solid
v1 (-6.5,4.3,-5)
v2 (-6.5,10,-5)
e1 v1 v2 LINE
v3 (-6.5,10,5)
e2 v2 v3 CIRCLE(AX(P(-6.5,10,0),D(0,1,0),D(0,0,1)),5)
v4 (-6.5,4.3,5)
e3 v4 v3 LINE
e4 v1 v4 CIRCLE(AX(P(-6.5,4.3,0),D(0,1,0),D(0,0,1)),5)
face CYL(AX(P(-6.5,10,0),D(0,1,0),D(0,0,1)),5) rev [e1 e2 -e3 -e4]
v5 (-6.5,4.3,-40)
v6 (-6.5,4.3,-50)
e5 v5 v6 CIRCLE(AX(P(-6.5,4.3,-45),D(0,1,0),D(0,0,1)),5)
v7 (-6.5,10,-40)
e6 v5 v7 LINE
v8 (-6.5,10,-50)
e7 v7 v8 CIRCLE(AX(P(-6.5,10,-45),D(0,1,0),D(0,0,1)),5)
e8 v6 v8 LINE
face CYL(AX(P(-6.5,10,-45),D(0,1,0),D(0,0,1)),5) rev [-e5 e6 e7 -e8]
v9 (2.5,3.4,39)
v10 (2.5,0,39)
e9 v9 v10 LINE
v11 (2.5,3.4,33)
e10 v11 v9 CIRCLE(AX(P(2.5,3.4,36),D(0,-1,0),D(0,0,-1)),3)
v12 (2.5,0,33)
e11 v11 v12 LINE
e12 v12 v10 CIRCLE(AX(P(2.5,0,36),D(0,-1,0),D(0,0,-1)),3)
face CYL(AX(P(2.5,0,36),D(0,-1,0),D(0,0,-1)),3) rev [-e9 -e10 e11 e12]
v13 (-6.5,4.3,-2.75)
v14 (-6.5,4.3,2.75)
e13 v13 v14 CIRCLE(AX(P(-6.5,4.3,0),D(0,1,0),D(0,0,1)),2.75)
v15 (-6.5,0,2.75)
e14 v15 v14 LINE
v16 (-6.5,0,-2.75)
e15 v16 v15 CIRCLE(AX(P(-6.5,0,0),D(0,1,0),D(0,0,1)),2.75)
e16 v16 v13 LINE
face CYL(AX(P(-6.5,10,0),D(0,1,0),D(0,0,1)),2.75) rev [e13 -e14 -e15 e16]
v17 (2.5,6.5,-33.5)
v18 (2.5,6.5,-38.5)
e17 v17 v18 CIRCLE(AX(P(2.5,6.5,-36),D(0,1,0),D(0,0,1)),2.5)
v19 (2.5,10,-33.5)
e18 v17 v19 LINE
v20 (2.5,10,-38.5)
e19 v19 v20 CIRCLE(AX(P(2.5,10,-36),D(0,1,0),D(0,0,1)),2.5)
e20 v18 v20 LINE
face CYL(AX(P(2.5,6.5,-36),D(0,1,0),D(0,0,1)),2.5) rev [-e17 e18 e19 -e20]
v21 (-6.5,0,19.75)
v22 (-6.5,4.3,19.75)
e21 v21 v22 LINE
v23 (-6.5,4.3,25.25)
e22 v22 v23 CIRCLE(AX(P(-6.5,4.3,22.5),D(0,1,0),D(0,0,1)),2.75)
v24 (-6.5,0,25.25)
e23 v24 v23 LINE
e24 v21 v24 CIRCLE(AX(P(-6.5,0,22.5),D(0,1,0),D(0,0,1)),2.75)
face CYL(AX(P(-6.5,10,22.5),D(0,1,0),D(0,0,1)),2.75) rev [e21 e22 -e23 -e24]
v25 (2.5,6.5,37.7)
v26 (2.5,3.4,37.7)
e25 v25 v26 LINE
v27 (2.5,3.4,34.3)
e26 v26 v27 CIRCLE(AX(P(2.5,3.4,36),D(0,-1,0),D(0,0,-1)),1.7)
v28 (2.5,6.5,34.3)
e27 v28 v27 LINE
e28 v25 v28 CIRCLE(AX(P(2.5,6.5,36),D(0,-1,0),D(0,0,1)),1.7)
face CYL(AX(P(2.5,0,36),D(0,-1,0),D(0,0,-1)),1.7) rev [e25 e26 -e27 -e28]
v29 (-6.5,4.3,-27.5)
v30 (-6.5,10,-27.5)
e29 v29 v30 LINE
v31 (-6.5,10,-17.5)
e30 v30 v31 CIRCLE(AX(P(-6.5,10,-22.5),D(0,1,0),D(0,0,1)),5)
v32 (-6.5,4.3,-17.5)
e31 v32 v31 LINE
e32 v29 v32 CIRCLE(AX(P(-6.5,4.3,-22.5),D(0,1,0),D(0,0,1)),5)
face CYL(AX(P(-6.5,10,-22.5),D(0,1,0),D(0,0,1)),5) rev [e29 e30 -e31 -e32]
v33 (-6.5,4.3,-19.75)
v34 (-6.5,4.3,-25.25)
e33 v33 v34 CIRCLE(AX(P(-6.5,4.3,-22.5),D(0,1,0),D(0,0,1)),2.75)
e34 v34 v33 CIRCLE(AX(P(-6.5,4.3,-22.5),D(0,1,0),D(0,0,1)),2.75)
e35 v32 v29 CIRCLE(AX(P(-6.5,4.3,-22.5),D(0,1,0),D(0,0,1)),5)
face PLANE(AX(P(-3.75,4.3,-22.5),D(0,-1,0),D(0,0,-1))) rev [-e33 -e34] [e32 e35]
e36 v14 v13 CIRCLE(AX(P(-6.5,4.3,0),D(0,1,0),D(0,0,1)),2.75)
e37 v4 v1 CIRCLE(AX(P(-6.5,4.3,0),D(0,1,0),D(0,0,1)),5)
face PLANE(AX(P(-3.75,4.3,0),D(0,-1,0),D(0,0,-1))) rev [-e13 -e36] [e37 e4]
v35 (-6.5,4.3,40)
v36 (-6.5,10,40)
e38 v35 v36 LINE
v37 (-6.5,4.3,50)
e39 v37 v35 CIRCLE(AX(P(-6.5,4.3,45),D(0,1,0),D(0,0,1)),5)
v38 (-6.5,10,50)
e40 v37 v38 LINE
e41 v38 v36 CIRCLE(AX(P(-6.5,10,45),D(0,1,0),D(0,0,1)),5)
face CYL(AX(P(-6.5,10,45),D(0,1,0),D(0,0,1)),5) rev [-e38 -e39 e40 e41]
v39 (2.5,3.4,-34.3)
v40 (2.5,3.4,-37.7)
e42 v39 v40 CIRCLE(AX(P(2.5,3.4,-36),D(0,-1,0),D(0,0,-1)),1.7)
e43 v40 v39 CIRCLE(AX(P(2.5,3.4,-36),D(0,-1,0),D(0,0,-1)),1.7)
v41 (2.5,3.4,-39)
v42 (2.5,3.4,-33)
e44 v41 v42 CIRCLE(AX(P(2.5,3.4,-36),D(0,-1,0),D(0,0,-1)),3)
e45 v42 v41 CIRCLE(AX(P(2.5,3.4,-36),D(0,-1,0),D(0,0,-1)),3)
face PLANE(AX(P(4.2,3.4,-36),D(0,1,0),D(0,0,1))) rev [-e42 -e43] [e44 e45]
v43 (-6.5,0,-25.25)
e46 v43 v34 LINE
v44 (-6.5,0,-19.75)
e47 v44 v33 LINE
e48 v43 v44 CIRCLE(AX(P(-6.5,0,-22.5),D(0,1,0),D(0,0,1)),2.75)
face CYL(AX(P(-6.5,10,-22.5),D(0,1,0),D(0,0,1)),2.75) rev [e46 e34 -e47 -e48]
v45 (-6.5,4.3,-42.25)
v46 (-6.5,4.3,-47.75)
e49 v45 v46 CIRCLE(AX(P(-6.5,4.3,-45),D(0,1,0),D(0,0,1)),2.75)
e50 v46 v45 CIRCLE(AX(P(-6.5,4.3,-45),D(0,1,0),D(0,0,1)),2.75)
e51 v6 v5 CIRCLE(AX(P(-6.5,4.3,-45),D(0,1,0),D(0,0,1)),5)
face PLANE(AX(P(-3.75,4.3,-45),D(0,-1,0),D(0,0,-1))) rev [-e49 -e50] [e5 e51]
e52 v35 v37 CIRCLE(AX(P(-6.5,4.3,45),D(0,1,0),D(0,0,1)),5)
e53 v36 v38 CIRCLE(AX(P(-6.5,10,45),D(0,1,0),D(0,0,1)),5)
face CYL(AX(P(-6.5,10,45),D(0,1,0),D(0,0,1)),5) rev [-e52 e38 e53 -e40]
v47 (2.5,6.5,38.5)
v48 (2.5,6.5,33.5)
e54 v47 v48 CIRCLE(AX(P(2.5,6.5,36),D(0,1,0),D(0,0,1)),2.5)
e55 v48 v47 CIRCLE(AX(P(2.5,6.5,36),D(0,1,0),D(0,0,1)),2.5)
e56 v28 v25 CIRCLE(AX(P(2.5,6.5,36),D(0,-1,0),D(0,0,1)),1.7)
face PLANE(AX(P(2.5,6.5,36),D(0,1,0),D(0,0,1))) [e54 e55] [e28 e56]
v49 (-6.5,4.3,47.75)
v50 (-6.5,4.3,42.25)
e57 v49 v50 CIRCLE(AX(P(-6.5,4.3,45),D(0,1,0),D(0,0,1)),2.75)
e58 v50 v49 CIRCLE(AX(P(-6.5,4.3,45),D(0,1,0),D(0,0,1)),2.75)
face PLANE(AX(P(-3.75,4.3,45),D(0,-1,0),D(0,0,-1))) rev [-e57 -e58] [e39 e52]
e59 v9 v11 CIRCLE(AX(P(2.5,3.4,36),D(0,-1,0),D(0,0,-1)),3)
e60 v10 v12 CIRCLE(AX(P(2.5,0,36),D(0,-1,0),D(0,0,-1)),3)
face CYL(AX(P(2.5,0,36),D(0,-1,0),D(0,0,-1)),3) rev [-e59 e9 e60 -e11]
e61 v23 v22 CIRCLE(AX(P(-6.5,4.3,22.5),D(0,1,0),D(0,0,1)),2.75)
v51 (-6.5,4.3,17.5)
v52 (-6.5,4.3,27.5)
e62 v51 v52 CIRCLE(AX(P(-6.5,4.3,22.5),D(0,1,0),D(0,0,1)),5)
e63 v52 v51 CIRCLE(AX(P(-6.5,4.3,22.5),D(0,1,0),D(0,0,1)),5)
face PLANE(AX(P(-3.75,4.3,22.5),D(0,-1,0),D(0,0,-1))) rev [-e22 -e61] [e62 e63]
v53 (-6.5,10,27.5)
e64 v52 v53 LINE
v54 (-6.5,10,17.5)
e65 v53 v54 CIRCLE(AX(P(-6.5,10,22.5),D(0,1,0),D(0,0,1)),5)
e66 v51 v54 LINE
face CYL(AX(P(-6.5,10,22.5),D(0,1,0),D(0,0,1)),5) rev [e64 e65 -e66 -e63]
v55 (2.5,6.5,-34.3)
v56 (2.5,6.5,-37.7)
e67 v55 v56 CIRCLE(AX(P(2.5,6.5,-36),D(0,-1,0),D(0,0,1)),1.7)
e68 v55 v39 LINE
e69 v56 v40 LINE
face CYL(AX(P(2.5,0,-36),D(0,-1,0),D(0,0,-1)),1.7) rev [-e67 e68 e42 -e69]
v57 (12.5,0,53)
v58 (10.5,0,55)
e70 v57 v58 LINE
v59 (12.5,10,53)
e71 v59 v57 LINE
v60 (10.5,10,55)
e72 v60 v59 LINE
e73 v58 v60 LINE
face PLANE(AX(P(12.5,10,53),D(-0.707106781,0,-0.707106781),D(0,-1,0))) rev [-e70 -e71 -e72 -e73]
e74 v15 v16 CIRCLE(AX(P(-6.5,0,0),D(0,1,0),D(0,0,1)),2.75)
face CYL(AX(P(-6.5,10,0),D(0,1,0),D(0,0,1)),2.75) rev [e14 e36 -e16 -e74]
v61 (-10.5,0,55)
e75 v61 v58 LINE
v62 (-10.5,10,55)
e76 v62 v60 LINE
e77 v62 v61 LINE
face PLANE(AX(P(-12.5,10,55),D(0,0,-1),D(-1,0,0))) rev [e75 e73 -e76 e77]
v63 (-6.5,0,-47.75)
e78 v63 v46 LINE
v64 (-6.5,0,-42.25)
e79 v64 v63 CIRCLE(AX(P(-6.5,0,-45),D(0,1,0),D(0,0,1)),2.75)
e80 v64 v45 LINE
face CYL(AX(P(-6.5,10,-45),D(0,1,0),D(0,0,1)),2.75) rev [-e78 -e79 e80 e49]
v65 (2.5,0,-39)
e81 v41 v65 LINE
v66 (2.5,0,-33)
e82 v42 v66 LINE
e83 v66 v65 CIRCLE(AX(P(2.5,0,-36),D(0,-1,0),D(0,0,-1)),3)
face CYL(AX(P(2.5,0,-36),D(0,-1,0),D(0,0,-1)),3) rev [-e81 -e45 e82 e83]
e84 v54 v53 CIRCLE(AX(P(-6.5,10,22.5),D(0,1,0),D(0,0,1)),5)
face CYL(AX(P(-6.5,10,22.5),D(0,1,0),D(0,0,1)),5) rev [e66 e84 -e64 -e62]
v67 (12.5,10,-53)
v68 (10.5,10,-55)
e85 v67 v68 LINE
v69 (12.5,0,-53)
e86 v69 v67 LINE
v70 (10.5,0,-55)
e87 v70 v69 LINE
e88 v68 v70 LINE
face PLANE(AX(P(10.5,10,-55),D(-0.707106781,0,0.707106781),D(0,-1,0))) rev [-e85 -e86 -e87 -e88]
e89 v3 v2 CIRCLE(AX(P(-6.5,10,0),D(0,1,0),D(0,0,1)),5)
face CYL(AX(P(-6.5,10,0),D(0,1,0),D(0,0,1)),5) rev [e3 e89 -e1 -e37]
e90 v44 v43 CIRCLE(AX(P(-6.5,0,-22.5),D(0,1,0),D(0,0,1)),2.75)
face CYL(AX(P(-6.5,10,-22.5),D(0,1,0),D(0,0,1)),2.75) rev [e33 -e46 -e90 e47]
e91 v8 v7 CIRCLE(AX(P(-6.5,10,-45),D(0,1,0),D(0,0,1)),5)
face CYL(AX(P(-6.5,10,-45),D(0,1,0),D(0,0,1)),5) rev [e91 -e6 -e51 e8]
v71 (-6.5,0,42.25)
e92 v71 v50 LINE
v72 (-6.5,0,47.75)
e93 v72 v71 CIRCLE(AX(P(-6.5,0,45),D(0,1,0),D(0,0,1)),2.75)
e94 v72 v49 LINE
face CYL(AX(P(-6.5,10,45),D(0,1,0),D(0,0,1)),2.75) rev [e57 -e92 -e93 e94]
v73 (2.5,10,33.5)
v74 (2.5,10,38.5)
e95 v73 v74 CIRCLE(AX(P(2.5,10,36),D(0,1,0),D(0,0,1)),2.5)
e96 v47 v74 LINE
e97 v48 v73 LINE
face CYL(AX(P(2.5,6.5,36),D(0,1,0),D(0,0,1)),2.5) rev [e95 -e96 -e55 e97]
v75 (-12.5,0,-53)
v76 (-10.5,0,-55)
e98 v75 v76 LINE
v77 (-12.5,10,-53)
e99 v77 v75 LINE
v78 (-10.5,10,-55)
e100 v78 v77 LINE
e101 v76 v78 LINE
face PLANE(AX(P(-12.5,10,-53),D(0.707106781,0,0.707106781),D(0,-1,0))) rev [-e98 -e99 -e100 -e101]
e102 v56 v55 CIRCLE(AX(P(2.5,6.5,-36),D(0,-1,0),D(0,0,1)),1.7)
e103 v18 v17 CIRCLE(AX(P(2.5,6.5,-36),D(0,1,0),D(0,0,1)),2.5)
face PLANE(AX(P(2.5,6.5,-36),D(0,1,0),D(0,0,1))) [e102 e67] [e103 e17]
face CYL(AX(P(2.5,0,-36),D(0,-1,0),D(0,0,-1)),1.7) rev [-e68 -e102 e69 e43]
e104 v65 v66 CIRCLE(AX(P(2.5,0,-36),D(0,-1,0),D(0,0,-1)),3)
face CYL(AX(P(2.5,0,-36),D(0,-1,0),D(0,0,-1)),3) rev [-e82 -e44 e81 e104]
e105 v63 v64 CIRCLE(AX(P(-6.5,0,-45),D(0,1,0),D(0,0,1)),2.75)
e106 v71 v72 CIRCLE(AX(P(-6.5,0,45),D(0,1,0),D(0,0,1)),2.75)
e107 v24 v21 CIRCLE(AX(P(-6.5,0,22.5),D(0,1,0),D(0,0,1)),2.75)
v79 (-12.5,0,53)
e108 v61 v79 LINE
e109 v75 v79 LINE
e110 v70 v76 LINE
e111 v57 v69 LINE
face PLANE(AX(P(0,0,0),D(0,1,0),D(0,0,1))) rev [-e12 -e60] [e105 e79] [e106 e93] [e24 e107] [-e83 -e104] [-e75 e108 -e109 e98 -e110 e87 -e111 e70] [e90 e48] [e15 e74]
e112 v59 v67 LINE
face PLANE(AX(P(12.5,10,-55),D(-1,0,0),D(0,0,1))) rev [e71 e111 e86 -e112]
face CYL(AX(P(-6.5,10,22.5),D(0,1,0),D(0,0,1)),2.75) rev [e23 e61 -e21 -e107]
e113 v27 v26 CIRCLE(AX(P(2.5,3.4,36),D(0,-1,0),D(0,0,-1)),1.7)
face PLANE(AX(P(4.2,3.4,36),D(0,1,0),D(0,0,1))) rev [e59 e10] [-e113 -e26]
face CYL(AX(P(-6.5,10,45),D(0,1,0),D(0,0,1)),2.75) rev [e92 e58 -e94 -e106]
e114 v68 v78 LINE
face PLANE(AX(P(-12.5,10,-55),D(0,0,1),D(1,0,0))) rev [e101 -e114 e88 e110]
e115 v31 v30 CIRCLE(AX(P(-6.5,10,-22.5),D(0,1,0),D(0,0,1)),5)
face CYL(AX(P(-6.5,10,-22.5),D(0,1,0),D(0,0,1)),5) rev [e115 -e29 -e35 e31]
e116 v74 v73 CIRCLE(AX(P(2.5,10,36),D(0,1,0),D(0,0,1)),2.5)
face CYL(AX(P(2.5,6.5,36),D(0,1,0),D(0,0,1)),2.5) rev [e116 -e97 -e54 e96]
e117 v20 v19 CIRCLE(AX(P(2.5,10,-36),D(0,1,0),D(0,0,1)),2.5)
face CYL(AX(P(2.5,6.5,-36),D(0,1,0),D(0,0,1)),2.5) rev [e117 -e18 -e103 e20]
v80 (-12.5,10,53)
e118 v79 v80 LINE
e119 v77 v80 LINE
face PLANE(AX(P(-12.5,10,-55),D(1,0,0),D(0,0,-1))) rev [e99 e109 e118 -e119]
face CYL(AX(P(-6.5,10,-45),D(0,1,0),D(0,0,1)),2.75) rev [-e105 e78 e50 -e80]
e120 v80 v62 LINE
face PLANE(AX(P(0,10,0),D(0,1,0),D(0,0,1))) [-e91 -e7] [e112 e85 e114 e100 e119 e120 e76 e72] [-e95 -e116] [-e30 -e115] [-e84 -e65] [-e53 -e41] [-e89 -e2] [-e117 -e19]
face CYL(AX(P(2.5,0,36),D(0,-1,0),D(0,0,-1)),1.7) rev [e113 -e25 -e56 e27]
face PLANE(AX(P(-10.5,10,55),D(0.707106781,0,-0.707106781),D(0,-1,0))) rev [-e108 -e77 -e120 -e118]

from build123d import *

# Parameters (mm, degrees)
SKETCH_1_W                  = 25
SKETCH_1_H                  = 110
EXTRUDE_1_DEPTH             = 10
CHAMFER_1_SIZE              = 2
HOLE_WIZARD_1_D             = 5.5
HOLE_WIZARD_1_DEPTH         = 12.4
HOLE_WIZARD_1_CBORE_D       = 10
HOLE_WIZARD_1_CBORE_DEPTH   = 5.7
HOLE_WIZARD_1_TIP           = 1.652366702
HOLE_WIZARD_1_2_D           = 3.4
HOLE_WIZARD_1_2_DEPTH       = 15
HOLE_WIZARD_1_2_CBORE_D     = 6
HOLE_WIZARD_1_2_CBORE_DEPTH = 3.4
HOLE_WIZARD_1_2_TIP         = 1.021463052
SKETCH_6_R                  = 2.5
CUT_EXTRUDE_1_DEPTH         = 3.5


with BuildPart() as part:
    # 草图1 → 凸台-拉伸1 (new body)
    with BuildSketch(Plane(origin=(0, 0, 0), x_dir=(1, 0, 0), z_dir=(0, 1, 0))):
        Rectangle(SKETCH_1_W, SKETCH_1_H)
    extrude(amount=EXTRUDE_1_DEPTH)

    # 倒角1
    chamfer_1_edges = [part.edges().sort_by_distance(p)[0] for p in [
        (12.5, 5, 55),
        (-12.5, 5, 55),
        (-12.5, 5, -55),
        (12.5, 5, -55),
    ]]
    chamfer(chamfer_1_edges, length=CHAMFER_1_SIZE)

    # Hole Wizard 1
    with Locations(Plane(origin=(0, 10, 0), x_dir=(1, 0, 0), z_dir=(0, 1, 0))):
        with Locations((-6.5, -45), (-6.5, 0), (-6.5, 45), (-6.5, -22.5), (-6.5, 22.5)):
            CounterBoreHole(HOLE_WIZARD_1_D / 2, HOLE_WIZARD_1_CBORE_D / 2, HOLE_WIZARD_1_CBORE_DEPTH, depth=HOLE_WIZARD_1_DEPTH)
            with Locations((0, 0, -(HOLE_WIZARD_1_DEPTH + HOLE_WIZARD_1_TIP / 2))):  # 118° drill point
                Cone(0, HOLE_WIZARD_1_D / 2, HOLE_WIZARD_1_TIP, mode=Mode.SUBTRACT)

    # Hole Wizard 1 2
    with Locations(Plane(origin=(0, 0, 0), x_dir=(-1, 0, 0), z_dir=(0, -1, 0))):
        with Locations((-2.5, -36), (-2.5, 36)):
            CounterBoreHole(HOLE_WIZARD_1_2_D / 2, HOLE_WIZARD_1_2_CBORE_D / 2, HOLE_WIZARD_1_2_CBORE_DEPTH, depth=HOLE_WIZARD_1_2_DEPTH)
            with Locations((0, 0, -(HOLE_WIZARD_1_2_DEPTH + HOLE_WIZARD_1_2_TIP / 2))):  # 118° drill point
                Cone(0, HOLE_WIZARD_1_2_D / 2, HOLE_WIZARD_1_2_TIP, mode=Mode.SUBTRACT)

    # 草图6 → 切除-拉伸1 (cut)
    with BuildSketch(Plane(origin=(0, 10, 0), x_dir=(1, 0, 0), z_dir=(0, 1, 0))):
        with Locations(Location((2.5, -36, 0), (0, 0, 270))):
            Circle(SKETCH_6_R)
        with Locations(Location((2.5, 36, 0), (0, 0, 270))):
            Circle(SKETCH_6_R)
    extrude(amount=-CUT_EXTRUDE_1_DEPTH, mode=Mode.SUBTRACT)


solid = part.part
